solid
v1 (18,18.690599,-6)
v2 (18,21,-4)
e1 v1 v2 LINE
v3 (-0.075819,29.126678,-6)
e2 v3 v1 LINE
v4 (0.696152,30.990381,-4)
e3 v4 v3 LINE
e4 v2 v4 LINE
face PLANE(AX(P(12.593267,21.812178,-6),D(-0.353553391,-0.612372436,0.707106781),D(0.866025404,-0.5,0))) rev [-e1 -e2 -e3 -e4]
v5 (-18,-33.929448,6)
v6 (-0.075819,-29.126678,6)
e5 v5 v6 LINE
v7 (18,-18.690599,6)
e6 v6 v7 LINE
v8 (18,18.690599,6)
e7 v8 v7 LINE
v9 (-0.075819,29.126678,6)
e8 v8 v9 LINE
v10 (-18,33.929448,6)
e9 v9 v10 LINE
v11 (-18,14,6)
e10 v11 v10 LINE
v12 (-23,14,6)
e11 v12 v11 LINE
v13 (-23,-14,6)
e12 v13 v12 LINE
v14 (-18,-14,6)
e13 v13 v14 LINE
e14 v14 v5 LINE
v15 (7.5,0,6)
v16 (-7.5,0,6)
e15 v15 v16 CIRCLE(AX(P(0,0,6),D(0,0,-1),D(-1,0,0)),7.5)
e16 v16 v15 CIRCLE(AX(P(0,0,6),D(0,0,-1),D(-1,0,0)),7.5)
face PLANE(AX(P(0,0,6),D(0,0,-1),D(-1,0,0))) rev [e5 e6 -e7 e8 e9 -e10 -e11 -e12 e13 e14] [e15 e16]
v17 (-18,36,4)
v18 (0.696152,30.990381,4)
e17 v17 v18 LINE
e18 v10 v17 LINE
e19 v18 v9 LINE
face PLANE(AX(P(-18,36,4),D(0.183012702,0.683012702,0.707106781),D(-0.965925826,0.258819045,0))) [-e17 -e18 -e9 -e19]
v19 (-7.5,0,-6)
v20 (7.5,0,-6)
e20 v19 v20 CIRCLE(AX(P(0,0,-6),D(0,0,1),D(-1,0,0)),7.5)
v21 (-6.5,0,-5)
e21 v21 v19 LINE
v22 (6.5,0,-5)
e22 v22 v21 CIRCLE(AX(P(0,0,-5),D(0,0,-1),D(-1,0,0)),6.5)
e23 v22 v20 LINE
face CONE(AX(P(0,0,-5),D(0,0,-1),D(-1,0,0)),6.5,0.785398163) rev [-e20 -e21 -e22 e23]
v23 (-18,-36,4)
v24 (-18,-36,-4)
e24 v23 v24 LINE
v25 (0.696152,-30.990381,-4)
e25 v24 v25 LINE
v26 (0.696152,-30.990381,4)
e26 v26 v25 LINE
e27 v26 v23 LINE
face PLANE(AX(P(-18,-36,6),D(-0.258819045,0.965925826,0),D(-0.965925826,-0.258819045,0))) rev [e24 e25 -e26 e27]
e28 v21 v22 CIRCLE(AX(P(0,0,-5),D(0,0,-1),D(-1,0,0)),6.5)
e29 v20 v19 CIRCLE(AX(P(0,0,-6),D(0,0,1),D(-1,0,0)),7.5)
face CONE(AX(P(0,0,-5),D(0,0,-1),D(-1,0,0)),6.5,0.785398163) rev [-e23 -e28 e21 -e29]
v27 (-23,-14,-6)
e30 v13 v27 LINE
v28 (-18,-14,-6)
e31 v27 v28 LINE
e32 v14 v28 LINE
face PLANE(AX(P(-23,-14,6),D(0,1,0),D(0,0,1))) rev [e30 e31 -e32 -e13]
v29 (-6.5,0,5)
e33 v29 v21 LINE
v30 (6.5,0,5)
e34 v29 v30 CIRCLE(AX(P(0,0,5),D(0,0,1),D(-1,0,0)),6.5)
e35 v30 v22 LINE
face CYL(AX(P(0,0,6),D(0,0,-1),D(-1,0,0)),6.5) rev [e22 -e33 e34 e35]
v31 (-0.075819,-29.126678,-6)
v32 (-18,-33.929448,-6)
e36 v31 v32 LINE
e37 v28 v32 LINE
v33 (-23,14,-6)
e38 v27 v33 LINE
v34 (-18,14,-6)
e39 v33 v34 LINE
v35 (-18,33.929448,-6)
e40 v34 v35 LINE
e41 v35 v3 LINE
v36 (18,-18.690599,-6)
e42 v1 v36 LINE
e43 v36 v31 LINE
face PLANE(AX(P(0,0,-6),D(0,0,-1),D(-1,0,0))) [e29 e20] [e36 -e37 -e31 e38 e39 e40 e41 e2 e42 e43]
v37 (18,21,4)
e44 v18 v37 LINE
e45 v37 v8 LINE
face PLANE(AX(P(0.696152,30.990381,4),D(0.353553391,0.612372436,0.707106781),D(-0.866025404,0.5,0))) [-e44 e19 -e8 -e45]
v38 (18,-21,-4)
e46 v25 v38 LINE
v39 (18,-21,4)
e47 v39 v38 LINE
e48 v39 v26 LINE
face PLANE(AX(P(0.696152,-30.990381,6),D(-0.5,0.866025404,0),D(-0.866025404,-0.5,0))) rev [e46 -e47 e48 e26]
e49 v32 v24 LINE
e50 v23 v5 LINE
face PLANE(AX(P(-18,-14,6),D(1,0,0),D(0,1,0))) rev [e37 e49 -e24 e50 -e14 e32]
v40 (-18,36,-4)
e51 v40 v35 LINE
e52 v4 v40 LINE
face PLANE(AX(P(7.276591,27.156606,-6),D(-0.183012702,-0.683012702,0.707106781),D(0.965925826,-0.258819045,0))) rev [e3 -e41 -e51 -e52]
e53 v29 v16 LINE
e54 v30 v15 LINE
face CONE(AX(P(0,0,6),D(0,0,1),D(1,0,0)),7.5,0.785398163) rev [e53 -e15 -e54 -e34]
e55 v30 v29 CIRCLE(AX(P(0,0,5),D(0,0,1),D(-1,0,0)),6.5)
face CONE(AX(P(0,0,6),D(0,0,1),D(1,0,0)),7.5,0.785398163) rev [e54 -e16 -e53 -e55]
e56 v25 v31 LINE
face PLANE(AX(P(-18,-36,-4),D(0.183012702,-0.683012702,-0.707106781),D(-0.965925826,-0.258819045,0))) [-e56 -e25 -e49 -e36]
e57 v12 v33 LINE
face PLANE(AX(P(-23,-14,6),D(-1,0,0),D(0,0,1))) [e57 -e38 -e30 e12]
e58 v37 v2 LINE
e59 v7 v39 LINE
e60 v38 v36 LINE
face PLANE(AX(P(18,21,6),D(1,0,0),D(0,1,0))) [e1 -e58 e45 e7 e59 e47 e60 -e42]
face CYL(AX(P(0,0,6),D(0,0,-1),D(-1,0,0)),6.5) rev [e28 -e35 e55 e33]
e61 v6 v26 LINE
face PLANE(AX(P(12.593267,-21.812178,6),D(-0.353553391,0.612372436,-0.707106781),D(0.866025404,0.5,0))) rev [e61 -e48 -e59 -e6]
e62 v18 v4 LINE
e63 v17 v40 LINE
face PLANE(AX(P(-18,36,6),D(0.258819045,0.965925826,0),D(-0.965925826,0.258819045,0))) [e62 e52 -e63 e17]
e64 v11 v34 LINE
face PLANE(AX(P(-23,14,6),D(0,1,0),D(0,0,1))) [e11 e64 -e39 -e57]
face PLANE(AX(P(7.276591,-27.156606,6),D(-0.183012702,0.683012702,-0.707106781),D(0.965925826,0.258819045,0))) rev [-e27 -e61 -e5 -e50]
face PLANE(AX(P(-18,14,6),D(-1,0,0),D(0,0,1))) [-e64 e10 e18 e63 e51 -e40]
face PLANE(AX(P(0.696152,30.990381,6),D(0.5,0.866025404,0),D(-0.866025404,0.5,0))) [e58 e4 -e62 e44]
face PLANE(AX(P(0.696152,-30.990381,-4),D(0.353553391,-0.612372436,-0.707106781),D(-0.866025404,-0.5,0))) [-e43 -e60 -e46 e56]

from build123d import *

# Parameters (mm, degrees)
SKETCH1_R           = 6.5
BOSS_EXTRUDE1_DEPTH = 6
CHAMFER1_SIZE       = 2
CHAMFER2_SIZE       = 1


with BuildPart() as part:
    # Sketch1 → Boss-Extrude1 (new, symmetric)
    with BuildSketch(Plane.XY):
        Polygon((-23, -14), (-23, 14), (-18, 14), (-18, 36), (0.696152423, 30.990381057), (18, 21), (18, -21), (0.696152423, -30.990381057), (-18, -36), (-18, -14), align=None)
        with Locations(Location((0, 0, 0), (0, 0, 180))):
            Circle(SKETCH1_R, mode=Mode.SUBTRACT)
    extrude(amount=BOSS_EXTRUDE1_DEPTH, both=True)

    # Chamfer1
    chamfer1_edges = [part.edges().sort_by_distance(p)[0] for p in [
        (-8.651923789, -33.495190528, -6),
        (9.348076211, -25.995190528, -6),
        (9.348076211, 25.995190528, 6),
        (9.348076211, 25.995190528, -6),
        (-8.651923789, 33.495190528, -6),
        (9.348076211, -25.995190528, 6),
        (-8.651923789, -33.495190528, 6),
        (-8.651923789, 33.495190528, 6),
    ]]
    chamfer(chamfer1_edges, length=CHAMFER1_SIZE)

    # Chamfer2
    chamfer2_edges = [part.edges().sort_by_distance(p)[0] for p in [
        (6.5, 0, 6),
        (6.5, 0, -6),
    ]]
    chamfer(chamfer2_edges, length=CHAMFER2_SIZE)


solid = part.part
